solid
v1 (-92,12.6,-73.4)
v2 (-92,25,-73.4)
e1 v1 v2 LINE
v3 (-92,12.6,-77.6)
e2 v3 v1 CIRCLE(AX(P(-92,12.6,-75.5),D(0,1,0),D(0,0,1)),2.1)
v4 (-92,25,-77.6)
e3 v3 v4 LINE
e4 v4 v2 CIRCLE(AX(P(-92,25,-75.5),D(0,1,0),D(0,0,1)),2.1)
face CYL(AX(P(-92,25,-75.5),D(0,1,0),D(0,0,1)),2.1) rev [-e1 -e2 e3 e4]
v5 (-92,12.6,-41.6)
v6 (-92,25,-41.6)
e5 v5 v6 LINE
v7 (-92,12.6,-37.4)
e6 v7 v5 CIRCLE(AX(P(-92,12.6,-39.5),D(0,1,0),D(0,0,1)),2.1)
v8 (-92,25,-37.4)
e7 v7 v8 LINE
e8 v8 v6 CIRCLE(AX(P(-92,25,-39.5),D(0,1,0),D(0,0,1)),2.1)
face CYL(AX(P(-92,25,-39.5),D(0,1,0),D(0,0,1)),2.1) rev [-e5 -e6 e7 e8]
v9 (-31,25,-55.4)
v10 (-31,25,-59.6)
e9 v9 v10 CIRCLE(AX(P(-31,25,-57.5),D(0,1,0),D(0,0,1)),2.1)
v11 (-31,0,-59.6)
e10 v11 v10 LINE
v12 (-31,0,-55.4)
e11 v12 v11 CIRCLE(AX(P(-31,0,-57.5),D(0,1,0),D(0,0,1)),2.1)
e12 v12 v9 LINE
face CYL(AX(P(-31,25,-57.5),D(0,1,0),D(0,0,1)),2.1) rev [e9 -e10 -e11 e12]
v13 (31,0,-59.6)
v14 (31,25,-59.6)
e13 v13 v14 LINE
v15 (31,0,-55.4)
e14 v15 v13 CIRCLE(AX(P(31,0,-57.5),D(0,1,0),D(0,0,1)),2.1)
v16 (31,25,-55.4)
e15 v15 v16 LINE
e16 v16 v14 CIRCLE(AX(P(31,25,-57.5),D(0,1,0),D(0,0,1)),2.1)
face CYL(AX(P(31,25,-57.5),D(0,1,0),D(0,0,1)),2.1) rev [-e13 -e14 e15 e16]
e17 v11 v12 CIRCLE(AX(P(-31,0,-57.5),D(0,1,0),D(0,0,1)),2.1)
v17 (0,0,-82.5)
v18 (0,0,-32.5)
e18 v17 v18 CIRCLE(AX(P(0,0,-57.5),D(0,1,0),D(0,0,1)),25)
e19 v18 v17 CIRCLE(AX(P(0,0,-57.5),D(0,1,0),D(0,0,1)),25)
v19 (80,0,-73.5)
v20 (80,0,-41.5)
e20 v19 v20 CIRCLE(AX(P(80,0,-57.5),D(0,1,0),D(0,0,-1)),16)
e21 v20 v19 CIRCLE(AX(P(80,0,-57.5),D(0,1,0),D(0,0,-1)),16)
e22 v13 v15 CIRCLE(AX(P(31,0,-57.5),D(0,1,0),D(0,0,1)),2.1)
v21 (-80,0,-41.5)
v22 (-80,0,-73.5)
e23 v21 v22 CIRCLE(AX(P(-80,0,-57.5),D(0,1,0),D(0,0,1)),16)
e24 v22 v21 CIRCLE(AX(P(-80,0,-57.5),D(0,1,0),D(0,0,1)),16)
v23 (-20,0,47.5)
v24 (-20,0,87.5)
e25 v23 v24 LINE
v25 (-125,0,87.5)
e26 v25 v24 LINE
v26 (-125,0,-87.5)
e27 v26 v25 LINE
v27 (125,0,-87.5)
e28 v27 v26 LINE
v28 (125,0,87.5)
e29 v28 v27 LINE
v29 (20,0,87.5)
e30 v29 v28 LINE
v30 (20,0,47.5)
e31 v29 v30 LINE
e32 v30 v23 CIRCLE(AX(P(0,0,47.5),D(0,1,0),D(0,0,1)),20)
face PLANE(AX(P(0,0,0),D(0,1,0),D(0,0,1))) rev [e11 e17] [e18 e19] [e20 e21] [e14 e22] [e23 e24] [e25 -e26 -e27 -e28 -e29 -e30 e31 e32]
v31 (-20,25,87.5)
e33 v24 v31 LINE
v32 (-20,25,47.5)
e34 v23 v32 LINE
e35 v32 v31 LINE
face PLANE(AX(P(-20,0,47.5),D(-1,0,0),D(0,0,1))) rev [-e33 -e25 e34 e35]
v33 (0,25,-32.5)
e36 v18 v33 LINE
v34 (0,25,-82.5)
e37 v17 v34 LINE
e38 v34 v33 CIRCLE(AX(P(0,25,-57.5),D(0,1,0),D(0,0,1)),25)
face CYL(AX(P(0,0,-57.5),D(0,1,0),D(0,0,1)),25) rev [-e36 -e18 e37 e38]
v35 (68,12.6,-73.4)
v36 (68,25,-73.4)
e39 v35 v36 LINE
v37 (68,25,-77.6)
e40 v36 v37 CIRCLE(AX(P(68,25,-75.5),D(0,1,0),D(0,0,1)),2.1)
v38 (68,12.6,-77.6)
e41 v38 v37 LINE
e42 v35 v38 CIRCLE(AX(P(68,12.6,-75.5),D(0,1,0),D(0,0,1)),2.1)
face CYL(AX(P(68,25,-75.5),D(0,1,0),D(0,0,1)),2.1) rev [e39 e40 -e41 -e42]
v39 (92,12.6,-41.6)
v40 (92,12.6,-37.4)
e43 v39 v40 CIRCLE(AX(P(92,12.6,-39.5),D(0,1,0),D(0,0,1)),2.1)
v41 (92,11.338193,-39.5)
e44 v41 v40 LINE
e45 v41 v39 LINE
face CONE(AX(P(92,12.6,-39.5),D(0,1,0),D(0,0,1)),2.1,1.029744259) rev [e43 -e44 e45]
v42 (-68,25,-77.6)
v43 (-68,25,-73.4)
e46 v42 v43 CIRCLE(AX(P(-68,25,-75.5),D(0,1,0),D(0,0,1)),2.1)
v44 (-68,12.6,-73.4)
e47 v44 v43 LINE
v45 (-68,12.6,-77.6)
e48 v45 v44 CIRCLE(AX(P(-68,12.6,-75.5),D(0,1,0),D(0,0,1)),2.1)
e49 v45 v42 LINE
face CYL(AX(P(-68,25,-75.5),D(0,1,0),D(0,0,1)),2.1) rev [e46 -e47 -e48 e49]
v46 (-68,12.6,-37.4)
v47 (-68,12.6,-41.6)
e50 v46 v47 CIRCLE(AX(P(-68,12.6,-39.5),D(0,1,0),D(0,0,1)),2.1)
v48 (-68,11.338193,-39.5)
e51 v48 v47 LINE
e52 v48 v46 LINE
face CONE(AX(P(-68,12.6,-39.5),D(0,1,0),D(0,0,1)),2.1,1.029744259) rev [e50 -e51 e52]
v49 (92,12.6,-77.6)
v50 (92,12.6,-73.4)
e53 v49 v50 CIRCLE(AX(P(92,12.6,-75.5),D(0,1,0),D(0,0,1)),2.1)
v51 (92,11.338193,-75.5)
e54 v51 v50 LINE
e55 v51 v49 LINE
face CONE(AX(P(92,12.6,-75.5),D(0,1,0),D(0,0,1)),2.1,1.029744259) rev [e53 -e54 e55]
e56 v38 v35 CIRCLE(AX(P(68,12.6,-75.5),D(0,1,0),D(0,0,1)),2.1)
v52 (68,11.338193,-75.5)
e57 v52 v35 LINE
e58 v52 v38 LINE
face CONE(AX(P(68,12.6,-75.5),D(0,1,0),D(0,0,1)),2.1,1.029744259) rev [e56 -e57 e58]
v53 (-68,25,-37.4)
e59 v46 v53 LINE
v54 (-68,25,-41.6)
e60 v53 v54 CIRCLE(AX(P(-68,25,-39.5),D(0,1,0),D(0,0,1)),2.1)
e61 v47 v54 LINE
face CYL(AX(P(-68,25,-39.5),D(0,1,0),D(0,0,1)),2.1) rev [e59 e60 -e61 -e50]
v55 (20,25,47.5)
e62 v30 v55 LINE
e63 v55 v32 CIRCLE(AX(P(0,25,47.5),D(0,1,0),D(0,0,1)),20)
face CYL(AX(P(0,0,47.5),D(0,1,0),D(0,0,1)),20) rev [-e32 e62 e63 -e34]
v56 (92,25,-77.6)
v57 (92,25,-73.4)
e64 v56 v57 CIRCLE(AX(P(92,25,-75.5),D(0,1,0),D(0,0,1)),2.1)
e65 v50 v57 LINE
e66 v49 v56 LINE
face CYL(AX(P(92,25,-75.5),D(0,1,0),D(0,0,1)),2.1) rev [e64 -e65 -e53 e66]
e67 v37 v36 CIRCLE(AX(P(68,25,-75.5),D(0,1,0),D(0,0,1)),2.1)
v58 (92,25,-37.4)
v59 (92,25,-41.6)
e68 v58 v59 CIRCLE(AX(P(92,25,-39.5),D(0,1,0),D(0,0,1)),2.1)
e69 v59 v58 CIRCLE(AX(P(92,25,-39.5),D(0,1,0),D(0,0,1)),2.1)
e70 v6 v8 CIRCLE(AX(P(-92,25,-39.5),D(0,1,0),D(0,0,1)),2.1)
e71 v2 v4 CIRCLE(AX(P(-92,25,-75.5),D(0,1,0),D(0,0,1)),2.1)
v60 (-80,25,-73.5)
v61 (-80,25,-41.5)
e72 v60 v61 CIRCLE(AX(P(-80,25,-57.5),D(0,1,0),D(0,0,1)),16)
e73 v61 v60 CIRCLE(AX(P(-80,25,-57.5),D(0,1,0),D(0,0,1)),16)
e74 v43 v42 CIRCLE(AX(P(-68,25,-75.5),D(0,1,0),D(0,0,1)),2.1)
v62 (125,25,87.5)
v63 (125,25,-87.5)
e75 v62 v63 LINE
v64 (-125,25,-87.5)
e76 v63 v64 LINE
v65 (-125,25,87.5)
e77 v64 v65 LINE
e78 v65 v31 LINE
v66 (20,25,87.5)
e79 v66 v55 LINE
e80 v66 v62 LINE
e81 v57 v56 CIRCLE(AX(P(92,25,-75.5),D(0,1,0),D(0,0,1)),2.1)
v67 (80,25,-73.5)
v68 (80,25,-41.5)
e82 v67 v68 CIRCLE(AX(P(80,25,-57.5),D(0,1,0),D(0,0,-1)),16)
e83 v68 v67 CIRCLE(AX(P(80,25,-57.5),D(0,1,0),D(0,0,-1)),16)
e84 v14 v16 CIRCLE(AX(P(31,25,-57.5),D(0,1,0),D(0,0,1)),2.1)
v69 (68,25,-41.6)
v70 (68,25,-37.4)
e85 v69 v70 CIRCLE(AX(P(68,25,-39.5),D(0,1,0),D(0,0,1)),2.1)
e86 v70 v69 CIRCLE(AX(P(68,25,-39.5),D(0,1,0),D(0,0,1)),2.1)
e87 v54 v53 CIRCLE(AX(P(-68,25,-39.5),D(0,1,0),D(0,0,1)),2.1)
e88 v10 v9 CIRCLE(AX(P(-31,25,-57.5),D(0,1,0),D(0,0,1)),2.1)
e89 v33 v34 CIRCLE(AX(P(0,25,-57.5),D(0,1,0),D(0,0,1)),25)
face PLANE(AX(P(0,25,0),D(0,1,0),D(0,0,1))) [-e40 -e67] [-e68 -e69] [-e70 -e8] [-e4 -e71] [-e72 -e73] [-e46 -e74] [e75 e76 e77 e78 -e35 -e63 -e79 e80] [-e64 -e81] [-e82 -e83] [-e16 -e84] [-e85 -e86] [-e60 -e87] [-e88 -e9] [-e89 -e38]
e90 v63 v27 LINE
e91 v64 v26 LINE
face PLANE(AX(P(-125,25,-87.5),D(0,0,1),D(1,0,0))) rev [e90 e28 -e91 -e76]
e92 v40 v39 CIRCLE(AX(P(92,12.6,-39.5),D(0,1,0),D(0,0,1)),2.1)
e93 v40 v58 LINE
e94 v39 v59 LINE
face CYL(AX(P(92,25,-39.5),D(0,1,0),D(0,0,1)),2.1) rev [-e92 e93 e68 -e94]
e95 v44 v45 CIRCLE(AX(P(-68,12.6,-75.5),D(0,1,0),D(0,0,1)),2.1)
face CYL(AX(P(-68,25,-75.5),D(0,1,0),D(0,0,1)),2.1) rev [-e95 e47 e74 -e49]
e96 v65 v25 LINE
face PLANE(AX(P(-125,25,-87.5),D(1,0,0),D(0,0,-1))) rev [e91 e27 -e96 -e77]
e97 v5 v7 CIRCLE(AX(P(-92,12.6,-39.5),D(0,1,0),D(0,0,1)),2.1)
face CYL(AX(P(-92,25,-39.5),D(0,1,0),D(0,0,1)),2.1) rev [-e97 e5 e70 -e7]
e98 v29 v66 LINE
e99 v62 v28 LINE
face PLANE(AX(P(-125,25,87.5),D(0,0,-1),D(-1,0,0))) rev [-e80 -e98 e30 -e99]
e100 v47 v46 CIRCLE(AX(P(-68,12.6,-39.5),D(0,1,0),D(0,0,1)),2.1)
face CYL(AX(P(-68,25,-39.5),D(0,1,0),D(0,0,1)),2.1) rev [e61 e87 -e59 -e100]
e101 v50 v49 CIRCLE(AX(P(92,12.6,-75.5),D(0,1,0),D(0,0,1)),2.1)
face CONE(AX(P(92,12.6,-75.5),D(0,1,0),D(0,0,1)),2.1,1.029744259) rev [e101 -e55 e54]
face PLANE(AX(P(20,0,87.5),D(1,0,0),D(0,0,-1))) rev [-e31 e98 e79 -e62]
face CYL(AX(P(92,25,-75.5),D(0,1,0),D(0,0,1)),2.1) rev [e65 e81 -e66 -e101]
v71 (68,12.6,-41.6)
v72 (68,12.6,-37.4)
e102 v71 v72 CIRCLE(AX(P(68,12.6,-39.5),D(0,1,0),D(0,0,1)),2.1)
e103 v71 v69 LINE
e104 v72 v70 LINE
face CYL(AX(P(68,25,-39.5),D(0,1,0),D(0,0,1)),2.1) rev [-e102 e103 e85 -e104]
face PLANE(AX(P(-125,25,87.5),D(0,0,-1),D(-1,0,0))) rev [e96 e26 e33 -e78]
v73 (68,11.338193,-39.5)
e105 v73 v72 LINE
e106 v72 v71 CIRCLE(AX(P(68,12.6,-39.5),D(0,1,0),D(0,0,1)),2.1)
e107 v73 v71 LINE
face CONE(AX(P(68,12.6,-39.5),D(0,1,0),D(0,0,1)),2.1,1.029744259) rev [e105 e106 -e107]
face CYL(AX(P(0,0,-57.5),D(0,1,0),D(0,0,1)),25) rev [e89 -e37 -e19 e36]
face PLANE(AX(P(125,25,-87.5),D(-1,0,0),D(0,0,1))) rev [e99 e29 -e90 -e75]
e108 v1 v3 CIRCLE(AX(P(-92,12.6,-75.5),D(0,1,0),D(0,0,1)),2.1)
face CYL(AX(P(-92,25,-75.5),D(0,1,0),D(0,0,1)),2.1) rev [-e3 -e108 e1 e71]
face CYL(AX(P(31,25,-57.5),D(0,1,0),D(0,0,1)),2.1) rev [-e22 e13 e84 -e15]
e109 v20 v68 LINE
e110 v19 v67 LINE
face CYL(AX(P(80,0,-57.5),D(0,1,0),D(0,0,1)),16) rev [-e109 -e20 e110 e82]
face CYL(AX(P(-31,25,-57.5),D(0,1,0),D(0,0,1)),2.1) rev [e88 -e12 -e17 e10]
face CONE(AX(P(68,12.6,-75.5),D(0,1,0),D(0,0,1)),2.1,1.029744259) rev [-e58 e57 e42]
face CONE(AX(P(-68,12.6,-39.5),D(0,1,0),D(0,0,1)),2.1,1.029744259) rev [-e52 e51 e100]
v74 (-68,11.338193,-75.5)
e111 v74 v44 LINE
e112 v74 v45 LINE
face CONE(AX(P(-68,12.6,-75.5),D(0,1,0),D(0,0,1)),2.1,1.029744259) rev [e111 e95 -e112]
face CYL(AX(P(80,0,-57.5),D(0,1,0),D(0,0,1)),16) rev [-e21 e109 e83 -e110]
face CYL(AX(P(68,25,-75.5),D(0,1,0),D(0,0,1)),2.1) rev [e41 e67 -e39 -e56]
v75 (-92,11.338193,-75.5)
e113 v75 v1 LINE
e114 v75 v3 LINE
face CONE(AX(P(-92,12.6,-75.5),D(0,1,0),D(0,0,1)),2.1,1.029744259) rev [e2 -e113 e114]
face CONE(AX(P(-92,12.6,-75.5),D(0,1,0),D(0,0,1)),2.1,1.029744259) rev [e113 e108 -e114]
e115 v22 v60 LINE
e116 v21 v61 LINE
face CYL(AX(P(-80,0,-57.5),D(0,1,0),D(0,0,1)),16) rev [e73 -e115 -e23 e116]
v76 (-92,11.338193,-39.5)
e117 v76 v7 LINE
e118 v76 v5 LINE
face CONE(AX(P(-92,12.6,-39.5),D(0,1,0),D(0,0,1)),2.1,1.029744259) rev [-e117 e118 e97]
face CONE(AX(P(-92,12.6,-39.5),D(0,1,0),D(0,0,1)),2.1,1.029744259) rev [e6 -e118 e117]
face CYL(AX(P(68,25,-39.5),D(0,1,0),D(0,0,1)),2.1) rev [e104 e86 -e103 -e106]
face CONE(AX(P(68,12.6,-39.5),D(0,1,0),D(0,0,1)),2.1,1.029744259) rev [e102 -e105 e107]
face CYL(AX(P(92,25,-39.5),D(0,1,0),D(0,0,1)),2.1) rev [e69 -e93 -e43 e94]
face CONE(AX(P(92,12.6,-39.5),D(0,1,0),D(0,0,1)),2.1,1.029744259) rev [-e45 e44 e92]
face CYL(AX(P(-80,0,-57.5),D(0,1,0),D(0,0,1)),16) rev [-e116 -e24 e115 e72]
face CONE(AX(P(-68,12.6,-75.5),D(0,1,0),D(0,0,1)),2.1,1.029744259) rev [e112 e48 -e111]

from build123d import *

# Parameters (mm, degrees)
SKETCH1_W                  = 250
SKETCH1_H                  = 175
BOSS_EXTRUDE1_DEPTH        = 25
CUT_EXTRUDE1_DEPTH         = 155.616460961
SKETCH3_R                  = 16
CUT_EXTRUDE2_DEPTH         = 155.616460961
M5_TAPPED_HOLE2_AT_2_COUNT = 2
M5_TAPPED_HOLE2_AT_2_PITCH = 24
M5_TAPPED_HOLE2_AT_3_COUNT = 2
M5_TAPPED_HOLE2_AT_3_PITCH = 36
M5_TAPPED_HOLE2_AT_4_COUNT = 2
M5_TAPPED_HOLE2_AT_4_PITCH = 43.266615306
SKETCH7_R                  = 25
CUT_EXTRUDE3_DEPTH         = 155.616460961
M5_TAPPED_HOLE1_D          = 4.2


with BuildPart() as part:
    # Sketch1 → Boss-Extrude1 (new body)
    with BuildSketch(Plane(origin=(0, 0, 0), x_dir=(1, 0, 0), z_dir=(0, 1, 0))):
        Rectangle(SKETCH1_W, SKETCH1_H)
    extrude(amount=BOSS_EXTRUDE1_DEPTH)

    # Sketch2 → Cut-Extrude1 (cut, through all)
    with BuildSketch(Plane(origin=(0, 25, 0), x_dir=(1, 0, 0), z_dir=(0, 1, 0))):
        with BuildLine():
            Line((-20, -47.5), (-20, -87.5))
            Line((-20, -87.5), (20, -87.5))
            Line((20, -87.5), (20, -47.5))
            ThreePointArc((20, -47.5), (0, -27.5), (-20, -47.5))
        make_face()
    extrude(amount=-CUT_EXTRUDE1_DEPTH, mode=Mode.SUBTRACT)

    # Sketch3 → Cut-Extrude2 (cut, through all)
    with BuildSketch(Plane(origin=(0, 25, 0), x_dir=(1, 0, 0), z_dir=(0, 1, 0))):
        with Locations(Location((-80, 57.5, 0), (0, 0, 270))):
            Circle(SKETCH3_R)
        with Locations(Location((80, 57.5, 0), (0, 0, 90))):
            Circle(SKETCH3_R)
    extrude(amount=-CUT_EXTRUDE2_DEPTH, mode=Mode.SUBTRACT)

    # Sketch6 → M5 Tapped Hole2 (revolve, cut)
    with BuildSketch(Plane(origin=(-92, 25, -75.5), x_dir=(0, 0, 1), z_dir=(1, 0, 0))):
        Polygon((0, 0), (0, 13.6618073), (2.1, 12.4), (2.1, 0), align=None)
    m5_tapped_hole2 = revolve(axis=Axis((-92, 31.35, -75.5), (0, -1, 0)), mode=Mode.SUBTRACT)

    # M5 Tapped Hole2 at 2: M5 Tapped Hole2 ×2
    with Locations(*[(i * M5_TAPPED_HOLE2_AT_2_PITCH, 0, 0) for i in range(1, M5_TAPPED_HOLE2_AT_2_COUNT)]):
        add(m5_tapped_hole2, mode=Mode.SUBTRACT)

    # M5 Tapped Hole2 at 3: M5 Tapped Hole2 ×2
    with Locations(*[(0, 0, i * M5_TAPPED_HOLE2_AT_3_PITCH) for i in range(1, M5_TAPPED_HOLE2_AT_3_COUNT)]):
        add(m5_tapped_hole2, mode=Mode.SUBTRACT)

    # M5 Tapped Hole2 at 4: M5 Tapped Hole2 ×2
    with Locations(*[Vector(0.5547001962252294, 0, 0.8320502943378435) * (i * M5_TAPPED_HOLE2_AT_4_PITCH) for i in range(1, M5_TAPPED_HOLE2_AT_4_COUNT)]):
        add(m5_tapped_hole2, mode=Mode.SUBTRACT)

    # Mirror1: M5 Tapped Hole2 across plane
    add(m5_tapped_hole2.mirror(Plane(origin=(0, 0, 0), x_dir=(0, 0, 1), z_dir=(1, 0, 0))), mode=Mode.SUBTRACT)

    # Mirror1 copy 1 sketch → Mirror1 copy 1 (revolve, cut)
    with BuildSketch(Plane(origin=(68, 25, -75.5), x_dir=(0, 0, 1), z_dir=(-1, 0, 0))):
        Polygon((0, 0), (0, -13.6618073), (2.1, -12.4), (2.1, 0), align=None)
    revolve(axis=Axis((68, 31.35, -75.5), (0, 1, 0)), mode=Mode.SUBTRACT)

    # Mirror1 copy 2 sketch → Mirror1 copy 2 (revolve, cut)
    with BuildSketch(Plane(origin=(92, 25, -39.5), x_dir=(0, 0, 1), z_dir=(-1, 0, 0))):
        Polygon((0, 0), (0, -13.6618073), (2.1, -12.4), (2.1, 0), align=None)
    revolve(axis=Axis((92, 31.35, -39.5), (0, 1, 0)), mode=Mode.SUBTRACT)

    # Mirror1 copy 3 sketch → Mirror1 copy 3 (revolve, cut)
    with BuildSketch(Plane(origin=(68, 25, -39.5), x_dir=(0, 0, 1), z_dir=(-1, 0, 0))):
        Polygon((0, 0), (0, -13.6618073), (2.1, -12.4), (2.1, 0), align=None)
    revolve(axis=Axis((68, 31.35, -39.5), (0, 1, 0)), mode=Mode.SUBTRACT)

    # Sketch7 → Cut-Extrude3 (cut, through all)
    with BuildSketch(Plane(origin=(0, 25, 0), x_dir=(1, 0, 0), z_dir=(0, 1, 0))):
        with Locations(Location((0, 57.5, 0), (0, 0, 270))):
            Circle(SKETCH7_R)
    extrude(amount=-CUT_EXTRUDE3_DEPTH, mode=Mode.SUBTRACT)

    # M5 Tapped Hole1 (through all)
    with Locations(Plane(origin=(0, 25, 0), x_dir=(1, 0, 0), z_dir=(0, 1, 0))):
        with Locations((-31, 57.5), (31, 57.5)):
            Hole(M5_TAPPED_HOLE1_D / 2)


solid = part.part
